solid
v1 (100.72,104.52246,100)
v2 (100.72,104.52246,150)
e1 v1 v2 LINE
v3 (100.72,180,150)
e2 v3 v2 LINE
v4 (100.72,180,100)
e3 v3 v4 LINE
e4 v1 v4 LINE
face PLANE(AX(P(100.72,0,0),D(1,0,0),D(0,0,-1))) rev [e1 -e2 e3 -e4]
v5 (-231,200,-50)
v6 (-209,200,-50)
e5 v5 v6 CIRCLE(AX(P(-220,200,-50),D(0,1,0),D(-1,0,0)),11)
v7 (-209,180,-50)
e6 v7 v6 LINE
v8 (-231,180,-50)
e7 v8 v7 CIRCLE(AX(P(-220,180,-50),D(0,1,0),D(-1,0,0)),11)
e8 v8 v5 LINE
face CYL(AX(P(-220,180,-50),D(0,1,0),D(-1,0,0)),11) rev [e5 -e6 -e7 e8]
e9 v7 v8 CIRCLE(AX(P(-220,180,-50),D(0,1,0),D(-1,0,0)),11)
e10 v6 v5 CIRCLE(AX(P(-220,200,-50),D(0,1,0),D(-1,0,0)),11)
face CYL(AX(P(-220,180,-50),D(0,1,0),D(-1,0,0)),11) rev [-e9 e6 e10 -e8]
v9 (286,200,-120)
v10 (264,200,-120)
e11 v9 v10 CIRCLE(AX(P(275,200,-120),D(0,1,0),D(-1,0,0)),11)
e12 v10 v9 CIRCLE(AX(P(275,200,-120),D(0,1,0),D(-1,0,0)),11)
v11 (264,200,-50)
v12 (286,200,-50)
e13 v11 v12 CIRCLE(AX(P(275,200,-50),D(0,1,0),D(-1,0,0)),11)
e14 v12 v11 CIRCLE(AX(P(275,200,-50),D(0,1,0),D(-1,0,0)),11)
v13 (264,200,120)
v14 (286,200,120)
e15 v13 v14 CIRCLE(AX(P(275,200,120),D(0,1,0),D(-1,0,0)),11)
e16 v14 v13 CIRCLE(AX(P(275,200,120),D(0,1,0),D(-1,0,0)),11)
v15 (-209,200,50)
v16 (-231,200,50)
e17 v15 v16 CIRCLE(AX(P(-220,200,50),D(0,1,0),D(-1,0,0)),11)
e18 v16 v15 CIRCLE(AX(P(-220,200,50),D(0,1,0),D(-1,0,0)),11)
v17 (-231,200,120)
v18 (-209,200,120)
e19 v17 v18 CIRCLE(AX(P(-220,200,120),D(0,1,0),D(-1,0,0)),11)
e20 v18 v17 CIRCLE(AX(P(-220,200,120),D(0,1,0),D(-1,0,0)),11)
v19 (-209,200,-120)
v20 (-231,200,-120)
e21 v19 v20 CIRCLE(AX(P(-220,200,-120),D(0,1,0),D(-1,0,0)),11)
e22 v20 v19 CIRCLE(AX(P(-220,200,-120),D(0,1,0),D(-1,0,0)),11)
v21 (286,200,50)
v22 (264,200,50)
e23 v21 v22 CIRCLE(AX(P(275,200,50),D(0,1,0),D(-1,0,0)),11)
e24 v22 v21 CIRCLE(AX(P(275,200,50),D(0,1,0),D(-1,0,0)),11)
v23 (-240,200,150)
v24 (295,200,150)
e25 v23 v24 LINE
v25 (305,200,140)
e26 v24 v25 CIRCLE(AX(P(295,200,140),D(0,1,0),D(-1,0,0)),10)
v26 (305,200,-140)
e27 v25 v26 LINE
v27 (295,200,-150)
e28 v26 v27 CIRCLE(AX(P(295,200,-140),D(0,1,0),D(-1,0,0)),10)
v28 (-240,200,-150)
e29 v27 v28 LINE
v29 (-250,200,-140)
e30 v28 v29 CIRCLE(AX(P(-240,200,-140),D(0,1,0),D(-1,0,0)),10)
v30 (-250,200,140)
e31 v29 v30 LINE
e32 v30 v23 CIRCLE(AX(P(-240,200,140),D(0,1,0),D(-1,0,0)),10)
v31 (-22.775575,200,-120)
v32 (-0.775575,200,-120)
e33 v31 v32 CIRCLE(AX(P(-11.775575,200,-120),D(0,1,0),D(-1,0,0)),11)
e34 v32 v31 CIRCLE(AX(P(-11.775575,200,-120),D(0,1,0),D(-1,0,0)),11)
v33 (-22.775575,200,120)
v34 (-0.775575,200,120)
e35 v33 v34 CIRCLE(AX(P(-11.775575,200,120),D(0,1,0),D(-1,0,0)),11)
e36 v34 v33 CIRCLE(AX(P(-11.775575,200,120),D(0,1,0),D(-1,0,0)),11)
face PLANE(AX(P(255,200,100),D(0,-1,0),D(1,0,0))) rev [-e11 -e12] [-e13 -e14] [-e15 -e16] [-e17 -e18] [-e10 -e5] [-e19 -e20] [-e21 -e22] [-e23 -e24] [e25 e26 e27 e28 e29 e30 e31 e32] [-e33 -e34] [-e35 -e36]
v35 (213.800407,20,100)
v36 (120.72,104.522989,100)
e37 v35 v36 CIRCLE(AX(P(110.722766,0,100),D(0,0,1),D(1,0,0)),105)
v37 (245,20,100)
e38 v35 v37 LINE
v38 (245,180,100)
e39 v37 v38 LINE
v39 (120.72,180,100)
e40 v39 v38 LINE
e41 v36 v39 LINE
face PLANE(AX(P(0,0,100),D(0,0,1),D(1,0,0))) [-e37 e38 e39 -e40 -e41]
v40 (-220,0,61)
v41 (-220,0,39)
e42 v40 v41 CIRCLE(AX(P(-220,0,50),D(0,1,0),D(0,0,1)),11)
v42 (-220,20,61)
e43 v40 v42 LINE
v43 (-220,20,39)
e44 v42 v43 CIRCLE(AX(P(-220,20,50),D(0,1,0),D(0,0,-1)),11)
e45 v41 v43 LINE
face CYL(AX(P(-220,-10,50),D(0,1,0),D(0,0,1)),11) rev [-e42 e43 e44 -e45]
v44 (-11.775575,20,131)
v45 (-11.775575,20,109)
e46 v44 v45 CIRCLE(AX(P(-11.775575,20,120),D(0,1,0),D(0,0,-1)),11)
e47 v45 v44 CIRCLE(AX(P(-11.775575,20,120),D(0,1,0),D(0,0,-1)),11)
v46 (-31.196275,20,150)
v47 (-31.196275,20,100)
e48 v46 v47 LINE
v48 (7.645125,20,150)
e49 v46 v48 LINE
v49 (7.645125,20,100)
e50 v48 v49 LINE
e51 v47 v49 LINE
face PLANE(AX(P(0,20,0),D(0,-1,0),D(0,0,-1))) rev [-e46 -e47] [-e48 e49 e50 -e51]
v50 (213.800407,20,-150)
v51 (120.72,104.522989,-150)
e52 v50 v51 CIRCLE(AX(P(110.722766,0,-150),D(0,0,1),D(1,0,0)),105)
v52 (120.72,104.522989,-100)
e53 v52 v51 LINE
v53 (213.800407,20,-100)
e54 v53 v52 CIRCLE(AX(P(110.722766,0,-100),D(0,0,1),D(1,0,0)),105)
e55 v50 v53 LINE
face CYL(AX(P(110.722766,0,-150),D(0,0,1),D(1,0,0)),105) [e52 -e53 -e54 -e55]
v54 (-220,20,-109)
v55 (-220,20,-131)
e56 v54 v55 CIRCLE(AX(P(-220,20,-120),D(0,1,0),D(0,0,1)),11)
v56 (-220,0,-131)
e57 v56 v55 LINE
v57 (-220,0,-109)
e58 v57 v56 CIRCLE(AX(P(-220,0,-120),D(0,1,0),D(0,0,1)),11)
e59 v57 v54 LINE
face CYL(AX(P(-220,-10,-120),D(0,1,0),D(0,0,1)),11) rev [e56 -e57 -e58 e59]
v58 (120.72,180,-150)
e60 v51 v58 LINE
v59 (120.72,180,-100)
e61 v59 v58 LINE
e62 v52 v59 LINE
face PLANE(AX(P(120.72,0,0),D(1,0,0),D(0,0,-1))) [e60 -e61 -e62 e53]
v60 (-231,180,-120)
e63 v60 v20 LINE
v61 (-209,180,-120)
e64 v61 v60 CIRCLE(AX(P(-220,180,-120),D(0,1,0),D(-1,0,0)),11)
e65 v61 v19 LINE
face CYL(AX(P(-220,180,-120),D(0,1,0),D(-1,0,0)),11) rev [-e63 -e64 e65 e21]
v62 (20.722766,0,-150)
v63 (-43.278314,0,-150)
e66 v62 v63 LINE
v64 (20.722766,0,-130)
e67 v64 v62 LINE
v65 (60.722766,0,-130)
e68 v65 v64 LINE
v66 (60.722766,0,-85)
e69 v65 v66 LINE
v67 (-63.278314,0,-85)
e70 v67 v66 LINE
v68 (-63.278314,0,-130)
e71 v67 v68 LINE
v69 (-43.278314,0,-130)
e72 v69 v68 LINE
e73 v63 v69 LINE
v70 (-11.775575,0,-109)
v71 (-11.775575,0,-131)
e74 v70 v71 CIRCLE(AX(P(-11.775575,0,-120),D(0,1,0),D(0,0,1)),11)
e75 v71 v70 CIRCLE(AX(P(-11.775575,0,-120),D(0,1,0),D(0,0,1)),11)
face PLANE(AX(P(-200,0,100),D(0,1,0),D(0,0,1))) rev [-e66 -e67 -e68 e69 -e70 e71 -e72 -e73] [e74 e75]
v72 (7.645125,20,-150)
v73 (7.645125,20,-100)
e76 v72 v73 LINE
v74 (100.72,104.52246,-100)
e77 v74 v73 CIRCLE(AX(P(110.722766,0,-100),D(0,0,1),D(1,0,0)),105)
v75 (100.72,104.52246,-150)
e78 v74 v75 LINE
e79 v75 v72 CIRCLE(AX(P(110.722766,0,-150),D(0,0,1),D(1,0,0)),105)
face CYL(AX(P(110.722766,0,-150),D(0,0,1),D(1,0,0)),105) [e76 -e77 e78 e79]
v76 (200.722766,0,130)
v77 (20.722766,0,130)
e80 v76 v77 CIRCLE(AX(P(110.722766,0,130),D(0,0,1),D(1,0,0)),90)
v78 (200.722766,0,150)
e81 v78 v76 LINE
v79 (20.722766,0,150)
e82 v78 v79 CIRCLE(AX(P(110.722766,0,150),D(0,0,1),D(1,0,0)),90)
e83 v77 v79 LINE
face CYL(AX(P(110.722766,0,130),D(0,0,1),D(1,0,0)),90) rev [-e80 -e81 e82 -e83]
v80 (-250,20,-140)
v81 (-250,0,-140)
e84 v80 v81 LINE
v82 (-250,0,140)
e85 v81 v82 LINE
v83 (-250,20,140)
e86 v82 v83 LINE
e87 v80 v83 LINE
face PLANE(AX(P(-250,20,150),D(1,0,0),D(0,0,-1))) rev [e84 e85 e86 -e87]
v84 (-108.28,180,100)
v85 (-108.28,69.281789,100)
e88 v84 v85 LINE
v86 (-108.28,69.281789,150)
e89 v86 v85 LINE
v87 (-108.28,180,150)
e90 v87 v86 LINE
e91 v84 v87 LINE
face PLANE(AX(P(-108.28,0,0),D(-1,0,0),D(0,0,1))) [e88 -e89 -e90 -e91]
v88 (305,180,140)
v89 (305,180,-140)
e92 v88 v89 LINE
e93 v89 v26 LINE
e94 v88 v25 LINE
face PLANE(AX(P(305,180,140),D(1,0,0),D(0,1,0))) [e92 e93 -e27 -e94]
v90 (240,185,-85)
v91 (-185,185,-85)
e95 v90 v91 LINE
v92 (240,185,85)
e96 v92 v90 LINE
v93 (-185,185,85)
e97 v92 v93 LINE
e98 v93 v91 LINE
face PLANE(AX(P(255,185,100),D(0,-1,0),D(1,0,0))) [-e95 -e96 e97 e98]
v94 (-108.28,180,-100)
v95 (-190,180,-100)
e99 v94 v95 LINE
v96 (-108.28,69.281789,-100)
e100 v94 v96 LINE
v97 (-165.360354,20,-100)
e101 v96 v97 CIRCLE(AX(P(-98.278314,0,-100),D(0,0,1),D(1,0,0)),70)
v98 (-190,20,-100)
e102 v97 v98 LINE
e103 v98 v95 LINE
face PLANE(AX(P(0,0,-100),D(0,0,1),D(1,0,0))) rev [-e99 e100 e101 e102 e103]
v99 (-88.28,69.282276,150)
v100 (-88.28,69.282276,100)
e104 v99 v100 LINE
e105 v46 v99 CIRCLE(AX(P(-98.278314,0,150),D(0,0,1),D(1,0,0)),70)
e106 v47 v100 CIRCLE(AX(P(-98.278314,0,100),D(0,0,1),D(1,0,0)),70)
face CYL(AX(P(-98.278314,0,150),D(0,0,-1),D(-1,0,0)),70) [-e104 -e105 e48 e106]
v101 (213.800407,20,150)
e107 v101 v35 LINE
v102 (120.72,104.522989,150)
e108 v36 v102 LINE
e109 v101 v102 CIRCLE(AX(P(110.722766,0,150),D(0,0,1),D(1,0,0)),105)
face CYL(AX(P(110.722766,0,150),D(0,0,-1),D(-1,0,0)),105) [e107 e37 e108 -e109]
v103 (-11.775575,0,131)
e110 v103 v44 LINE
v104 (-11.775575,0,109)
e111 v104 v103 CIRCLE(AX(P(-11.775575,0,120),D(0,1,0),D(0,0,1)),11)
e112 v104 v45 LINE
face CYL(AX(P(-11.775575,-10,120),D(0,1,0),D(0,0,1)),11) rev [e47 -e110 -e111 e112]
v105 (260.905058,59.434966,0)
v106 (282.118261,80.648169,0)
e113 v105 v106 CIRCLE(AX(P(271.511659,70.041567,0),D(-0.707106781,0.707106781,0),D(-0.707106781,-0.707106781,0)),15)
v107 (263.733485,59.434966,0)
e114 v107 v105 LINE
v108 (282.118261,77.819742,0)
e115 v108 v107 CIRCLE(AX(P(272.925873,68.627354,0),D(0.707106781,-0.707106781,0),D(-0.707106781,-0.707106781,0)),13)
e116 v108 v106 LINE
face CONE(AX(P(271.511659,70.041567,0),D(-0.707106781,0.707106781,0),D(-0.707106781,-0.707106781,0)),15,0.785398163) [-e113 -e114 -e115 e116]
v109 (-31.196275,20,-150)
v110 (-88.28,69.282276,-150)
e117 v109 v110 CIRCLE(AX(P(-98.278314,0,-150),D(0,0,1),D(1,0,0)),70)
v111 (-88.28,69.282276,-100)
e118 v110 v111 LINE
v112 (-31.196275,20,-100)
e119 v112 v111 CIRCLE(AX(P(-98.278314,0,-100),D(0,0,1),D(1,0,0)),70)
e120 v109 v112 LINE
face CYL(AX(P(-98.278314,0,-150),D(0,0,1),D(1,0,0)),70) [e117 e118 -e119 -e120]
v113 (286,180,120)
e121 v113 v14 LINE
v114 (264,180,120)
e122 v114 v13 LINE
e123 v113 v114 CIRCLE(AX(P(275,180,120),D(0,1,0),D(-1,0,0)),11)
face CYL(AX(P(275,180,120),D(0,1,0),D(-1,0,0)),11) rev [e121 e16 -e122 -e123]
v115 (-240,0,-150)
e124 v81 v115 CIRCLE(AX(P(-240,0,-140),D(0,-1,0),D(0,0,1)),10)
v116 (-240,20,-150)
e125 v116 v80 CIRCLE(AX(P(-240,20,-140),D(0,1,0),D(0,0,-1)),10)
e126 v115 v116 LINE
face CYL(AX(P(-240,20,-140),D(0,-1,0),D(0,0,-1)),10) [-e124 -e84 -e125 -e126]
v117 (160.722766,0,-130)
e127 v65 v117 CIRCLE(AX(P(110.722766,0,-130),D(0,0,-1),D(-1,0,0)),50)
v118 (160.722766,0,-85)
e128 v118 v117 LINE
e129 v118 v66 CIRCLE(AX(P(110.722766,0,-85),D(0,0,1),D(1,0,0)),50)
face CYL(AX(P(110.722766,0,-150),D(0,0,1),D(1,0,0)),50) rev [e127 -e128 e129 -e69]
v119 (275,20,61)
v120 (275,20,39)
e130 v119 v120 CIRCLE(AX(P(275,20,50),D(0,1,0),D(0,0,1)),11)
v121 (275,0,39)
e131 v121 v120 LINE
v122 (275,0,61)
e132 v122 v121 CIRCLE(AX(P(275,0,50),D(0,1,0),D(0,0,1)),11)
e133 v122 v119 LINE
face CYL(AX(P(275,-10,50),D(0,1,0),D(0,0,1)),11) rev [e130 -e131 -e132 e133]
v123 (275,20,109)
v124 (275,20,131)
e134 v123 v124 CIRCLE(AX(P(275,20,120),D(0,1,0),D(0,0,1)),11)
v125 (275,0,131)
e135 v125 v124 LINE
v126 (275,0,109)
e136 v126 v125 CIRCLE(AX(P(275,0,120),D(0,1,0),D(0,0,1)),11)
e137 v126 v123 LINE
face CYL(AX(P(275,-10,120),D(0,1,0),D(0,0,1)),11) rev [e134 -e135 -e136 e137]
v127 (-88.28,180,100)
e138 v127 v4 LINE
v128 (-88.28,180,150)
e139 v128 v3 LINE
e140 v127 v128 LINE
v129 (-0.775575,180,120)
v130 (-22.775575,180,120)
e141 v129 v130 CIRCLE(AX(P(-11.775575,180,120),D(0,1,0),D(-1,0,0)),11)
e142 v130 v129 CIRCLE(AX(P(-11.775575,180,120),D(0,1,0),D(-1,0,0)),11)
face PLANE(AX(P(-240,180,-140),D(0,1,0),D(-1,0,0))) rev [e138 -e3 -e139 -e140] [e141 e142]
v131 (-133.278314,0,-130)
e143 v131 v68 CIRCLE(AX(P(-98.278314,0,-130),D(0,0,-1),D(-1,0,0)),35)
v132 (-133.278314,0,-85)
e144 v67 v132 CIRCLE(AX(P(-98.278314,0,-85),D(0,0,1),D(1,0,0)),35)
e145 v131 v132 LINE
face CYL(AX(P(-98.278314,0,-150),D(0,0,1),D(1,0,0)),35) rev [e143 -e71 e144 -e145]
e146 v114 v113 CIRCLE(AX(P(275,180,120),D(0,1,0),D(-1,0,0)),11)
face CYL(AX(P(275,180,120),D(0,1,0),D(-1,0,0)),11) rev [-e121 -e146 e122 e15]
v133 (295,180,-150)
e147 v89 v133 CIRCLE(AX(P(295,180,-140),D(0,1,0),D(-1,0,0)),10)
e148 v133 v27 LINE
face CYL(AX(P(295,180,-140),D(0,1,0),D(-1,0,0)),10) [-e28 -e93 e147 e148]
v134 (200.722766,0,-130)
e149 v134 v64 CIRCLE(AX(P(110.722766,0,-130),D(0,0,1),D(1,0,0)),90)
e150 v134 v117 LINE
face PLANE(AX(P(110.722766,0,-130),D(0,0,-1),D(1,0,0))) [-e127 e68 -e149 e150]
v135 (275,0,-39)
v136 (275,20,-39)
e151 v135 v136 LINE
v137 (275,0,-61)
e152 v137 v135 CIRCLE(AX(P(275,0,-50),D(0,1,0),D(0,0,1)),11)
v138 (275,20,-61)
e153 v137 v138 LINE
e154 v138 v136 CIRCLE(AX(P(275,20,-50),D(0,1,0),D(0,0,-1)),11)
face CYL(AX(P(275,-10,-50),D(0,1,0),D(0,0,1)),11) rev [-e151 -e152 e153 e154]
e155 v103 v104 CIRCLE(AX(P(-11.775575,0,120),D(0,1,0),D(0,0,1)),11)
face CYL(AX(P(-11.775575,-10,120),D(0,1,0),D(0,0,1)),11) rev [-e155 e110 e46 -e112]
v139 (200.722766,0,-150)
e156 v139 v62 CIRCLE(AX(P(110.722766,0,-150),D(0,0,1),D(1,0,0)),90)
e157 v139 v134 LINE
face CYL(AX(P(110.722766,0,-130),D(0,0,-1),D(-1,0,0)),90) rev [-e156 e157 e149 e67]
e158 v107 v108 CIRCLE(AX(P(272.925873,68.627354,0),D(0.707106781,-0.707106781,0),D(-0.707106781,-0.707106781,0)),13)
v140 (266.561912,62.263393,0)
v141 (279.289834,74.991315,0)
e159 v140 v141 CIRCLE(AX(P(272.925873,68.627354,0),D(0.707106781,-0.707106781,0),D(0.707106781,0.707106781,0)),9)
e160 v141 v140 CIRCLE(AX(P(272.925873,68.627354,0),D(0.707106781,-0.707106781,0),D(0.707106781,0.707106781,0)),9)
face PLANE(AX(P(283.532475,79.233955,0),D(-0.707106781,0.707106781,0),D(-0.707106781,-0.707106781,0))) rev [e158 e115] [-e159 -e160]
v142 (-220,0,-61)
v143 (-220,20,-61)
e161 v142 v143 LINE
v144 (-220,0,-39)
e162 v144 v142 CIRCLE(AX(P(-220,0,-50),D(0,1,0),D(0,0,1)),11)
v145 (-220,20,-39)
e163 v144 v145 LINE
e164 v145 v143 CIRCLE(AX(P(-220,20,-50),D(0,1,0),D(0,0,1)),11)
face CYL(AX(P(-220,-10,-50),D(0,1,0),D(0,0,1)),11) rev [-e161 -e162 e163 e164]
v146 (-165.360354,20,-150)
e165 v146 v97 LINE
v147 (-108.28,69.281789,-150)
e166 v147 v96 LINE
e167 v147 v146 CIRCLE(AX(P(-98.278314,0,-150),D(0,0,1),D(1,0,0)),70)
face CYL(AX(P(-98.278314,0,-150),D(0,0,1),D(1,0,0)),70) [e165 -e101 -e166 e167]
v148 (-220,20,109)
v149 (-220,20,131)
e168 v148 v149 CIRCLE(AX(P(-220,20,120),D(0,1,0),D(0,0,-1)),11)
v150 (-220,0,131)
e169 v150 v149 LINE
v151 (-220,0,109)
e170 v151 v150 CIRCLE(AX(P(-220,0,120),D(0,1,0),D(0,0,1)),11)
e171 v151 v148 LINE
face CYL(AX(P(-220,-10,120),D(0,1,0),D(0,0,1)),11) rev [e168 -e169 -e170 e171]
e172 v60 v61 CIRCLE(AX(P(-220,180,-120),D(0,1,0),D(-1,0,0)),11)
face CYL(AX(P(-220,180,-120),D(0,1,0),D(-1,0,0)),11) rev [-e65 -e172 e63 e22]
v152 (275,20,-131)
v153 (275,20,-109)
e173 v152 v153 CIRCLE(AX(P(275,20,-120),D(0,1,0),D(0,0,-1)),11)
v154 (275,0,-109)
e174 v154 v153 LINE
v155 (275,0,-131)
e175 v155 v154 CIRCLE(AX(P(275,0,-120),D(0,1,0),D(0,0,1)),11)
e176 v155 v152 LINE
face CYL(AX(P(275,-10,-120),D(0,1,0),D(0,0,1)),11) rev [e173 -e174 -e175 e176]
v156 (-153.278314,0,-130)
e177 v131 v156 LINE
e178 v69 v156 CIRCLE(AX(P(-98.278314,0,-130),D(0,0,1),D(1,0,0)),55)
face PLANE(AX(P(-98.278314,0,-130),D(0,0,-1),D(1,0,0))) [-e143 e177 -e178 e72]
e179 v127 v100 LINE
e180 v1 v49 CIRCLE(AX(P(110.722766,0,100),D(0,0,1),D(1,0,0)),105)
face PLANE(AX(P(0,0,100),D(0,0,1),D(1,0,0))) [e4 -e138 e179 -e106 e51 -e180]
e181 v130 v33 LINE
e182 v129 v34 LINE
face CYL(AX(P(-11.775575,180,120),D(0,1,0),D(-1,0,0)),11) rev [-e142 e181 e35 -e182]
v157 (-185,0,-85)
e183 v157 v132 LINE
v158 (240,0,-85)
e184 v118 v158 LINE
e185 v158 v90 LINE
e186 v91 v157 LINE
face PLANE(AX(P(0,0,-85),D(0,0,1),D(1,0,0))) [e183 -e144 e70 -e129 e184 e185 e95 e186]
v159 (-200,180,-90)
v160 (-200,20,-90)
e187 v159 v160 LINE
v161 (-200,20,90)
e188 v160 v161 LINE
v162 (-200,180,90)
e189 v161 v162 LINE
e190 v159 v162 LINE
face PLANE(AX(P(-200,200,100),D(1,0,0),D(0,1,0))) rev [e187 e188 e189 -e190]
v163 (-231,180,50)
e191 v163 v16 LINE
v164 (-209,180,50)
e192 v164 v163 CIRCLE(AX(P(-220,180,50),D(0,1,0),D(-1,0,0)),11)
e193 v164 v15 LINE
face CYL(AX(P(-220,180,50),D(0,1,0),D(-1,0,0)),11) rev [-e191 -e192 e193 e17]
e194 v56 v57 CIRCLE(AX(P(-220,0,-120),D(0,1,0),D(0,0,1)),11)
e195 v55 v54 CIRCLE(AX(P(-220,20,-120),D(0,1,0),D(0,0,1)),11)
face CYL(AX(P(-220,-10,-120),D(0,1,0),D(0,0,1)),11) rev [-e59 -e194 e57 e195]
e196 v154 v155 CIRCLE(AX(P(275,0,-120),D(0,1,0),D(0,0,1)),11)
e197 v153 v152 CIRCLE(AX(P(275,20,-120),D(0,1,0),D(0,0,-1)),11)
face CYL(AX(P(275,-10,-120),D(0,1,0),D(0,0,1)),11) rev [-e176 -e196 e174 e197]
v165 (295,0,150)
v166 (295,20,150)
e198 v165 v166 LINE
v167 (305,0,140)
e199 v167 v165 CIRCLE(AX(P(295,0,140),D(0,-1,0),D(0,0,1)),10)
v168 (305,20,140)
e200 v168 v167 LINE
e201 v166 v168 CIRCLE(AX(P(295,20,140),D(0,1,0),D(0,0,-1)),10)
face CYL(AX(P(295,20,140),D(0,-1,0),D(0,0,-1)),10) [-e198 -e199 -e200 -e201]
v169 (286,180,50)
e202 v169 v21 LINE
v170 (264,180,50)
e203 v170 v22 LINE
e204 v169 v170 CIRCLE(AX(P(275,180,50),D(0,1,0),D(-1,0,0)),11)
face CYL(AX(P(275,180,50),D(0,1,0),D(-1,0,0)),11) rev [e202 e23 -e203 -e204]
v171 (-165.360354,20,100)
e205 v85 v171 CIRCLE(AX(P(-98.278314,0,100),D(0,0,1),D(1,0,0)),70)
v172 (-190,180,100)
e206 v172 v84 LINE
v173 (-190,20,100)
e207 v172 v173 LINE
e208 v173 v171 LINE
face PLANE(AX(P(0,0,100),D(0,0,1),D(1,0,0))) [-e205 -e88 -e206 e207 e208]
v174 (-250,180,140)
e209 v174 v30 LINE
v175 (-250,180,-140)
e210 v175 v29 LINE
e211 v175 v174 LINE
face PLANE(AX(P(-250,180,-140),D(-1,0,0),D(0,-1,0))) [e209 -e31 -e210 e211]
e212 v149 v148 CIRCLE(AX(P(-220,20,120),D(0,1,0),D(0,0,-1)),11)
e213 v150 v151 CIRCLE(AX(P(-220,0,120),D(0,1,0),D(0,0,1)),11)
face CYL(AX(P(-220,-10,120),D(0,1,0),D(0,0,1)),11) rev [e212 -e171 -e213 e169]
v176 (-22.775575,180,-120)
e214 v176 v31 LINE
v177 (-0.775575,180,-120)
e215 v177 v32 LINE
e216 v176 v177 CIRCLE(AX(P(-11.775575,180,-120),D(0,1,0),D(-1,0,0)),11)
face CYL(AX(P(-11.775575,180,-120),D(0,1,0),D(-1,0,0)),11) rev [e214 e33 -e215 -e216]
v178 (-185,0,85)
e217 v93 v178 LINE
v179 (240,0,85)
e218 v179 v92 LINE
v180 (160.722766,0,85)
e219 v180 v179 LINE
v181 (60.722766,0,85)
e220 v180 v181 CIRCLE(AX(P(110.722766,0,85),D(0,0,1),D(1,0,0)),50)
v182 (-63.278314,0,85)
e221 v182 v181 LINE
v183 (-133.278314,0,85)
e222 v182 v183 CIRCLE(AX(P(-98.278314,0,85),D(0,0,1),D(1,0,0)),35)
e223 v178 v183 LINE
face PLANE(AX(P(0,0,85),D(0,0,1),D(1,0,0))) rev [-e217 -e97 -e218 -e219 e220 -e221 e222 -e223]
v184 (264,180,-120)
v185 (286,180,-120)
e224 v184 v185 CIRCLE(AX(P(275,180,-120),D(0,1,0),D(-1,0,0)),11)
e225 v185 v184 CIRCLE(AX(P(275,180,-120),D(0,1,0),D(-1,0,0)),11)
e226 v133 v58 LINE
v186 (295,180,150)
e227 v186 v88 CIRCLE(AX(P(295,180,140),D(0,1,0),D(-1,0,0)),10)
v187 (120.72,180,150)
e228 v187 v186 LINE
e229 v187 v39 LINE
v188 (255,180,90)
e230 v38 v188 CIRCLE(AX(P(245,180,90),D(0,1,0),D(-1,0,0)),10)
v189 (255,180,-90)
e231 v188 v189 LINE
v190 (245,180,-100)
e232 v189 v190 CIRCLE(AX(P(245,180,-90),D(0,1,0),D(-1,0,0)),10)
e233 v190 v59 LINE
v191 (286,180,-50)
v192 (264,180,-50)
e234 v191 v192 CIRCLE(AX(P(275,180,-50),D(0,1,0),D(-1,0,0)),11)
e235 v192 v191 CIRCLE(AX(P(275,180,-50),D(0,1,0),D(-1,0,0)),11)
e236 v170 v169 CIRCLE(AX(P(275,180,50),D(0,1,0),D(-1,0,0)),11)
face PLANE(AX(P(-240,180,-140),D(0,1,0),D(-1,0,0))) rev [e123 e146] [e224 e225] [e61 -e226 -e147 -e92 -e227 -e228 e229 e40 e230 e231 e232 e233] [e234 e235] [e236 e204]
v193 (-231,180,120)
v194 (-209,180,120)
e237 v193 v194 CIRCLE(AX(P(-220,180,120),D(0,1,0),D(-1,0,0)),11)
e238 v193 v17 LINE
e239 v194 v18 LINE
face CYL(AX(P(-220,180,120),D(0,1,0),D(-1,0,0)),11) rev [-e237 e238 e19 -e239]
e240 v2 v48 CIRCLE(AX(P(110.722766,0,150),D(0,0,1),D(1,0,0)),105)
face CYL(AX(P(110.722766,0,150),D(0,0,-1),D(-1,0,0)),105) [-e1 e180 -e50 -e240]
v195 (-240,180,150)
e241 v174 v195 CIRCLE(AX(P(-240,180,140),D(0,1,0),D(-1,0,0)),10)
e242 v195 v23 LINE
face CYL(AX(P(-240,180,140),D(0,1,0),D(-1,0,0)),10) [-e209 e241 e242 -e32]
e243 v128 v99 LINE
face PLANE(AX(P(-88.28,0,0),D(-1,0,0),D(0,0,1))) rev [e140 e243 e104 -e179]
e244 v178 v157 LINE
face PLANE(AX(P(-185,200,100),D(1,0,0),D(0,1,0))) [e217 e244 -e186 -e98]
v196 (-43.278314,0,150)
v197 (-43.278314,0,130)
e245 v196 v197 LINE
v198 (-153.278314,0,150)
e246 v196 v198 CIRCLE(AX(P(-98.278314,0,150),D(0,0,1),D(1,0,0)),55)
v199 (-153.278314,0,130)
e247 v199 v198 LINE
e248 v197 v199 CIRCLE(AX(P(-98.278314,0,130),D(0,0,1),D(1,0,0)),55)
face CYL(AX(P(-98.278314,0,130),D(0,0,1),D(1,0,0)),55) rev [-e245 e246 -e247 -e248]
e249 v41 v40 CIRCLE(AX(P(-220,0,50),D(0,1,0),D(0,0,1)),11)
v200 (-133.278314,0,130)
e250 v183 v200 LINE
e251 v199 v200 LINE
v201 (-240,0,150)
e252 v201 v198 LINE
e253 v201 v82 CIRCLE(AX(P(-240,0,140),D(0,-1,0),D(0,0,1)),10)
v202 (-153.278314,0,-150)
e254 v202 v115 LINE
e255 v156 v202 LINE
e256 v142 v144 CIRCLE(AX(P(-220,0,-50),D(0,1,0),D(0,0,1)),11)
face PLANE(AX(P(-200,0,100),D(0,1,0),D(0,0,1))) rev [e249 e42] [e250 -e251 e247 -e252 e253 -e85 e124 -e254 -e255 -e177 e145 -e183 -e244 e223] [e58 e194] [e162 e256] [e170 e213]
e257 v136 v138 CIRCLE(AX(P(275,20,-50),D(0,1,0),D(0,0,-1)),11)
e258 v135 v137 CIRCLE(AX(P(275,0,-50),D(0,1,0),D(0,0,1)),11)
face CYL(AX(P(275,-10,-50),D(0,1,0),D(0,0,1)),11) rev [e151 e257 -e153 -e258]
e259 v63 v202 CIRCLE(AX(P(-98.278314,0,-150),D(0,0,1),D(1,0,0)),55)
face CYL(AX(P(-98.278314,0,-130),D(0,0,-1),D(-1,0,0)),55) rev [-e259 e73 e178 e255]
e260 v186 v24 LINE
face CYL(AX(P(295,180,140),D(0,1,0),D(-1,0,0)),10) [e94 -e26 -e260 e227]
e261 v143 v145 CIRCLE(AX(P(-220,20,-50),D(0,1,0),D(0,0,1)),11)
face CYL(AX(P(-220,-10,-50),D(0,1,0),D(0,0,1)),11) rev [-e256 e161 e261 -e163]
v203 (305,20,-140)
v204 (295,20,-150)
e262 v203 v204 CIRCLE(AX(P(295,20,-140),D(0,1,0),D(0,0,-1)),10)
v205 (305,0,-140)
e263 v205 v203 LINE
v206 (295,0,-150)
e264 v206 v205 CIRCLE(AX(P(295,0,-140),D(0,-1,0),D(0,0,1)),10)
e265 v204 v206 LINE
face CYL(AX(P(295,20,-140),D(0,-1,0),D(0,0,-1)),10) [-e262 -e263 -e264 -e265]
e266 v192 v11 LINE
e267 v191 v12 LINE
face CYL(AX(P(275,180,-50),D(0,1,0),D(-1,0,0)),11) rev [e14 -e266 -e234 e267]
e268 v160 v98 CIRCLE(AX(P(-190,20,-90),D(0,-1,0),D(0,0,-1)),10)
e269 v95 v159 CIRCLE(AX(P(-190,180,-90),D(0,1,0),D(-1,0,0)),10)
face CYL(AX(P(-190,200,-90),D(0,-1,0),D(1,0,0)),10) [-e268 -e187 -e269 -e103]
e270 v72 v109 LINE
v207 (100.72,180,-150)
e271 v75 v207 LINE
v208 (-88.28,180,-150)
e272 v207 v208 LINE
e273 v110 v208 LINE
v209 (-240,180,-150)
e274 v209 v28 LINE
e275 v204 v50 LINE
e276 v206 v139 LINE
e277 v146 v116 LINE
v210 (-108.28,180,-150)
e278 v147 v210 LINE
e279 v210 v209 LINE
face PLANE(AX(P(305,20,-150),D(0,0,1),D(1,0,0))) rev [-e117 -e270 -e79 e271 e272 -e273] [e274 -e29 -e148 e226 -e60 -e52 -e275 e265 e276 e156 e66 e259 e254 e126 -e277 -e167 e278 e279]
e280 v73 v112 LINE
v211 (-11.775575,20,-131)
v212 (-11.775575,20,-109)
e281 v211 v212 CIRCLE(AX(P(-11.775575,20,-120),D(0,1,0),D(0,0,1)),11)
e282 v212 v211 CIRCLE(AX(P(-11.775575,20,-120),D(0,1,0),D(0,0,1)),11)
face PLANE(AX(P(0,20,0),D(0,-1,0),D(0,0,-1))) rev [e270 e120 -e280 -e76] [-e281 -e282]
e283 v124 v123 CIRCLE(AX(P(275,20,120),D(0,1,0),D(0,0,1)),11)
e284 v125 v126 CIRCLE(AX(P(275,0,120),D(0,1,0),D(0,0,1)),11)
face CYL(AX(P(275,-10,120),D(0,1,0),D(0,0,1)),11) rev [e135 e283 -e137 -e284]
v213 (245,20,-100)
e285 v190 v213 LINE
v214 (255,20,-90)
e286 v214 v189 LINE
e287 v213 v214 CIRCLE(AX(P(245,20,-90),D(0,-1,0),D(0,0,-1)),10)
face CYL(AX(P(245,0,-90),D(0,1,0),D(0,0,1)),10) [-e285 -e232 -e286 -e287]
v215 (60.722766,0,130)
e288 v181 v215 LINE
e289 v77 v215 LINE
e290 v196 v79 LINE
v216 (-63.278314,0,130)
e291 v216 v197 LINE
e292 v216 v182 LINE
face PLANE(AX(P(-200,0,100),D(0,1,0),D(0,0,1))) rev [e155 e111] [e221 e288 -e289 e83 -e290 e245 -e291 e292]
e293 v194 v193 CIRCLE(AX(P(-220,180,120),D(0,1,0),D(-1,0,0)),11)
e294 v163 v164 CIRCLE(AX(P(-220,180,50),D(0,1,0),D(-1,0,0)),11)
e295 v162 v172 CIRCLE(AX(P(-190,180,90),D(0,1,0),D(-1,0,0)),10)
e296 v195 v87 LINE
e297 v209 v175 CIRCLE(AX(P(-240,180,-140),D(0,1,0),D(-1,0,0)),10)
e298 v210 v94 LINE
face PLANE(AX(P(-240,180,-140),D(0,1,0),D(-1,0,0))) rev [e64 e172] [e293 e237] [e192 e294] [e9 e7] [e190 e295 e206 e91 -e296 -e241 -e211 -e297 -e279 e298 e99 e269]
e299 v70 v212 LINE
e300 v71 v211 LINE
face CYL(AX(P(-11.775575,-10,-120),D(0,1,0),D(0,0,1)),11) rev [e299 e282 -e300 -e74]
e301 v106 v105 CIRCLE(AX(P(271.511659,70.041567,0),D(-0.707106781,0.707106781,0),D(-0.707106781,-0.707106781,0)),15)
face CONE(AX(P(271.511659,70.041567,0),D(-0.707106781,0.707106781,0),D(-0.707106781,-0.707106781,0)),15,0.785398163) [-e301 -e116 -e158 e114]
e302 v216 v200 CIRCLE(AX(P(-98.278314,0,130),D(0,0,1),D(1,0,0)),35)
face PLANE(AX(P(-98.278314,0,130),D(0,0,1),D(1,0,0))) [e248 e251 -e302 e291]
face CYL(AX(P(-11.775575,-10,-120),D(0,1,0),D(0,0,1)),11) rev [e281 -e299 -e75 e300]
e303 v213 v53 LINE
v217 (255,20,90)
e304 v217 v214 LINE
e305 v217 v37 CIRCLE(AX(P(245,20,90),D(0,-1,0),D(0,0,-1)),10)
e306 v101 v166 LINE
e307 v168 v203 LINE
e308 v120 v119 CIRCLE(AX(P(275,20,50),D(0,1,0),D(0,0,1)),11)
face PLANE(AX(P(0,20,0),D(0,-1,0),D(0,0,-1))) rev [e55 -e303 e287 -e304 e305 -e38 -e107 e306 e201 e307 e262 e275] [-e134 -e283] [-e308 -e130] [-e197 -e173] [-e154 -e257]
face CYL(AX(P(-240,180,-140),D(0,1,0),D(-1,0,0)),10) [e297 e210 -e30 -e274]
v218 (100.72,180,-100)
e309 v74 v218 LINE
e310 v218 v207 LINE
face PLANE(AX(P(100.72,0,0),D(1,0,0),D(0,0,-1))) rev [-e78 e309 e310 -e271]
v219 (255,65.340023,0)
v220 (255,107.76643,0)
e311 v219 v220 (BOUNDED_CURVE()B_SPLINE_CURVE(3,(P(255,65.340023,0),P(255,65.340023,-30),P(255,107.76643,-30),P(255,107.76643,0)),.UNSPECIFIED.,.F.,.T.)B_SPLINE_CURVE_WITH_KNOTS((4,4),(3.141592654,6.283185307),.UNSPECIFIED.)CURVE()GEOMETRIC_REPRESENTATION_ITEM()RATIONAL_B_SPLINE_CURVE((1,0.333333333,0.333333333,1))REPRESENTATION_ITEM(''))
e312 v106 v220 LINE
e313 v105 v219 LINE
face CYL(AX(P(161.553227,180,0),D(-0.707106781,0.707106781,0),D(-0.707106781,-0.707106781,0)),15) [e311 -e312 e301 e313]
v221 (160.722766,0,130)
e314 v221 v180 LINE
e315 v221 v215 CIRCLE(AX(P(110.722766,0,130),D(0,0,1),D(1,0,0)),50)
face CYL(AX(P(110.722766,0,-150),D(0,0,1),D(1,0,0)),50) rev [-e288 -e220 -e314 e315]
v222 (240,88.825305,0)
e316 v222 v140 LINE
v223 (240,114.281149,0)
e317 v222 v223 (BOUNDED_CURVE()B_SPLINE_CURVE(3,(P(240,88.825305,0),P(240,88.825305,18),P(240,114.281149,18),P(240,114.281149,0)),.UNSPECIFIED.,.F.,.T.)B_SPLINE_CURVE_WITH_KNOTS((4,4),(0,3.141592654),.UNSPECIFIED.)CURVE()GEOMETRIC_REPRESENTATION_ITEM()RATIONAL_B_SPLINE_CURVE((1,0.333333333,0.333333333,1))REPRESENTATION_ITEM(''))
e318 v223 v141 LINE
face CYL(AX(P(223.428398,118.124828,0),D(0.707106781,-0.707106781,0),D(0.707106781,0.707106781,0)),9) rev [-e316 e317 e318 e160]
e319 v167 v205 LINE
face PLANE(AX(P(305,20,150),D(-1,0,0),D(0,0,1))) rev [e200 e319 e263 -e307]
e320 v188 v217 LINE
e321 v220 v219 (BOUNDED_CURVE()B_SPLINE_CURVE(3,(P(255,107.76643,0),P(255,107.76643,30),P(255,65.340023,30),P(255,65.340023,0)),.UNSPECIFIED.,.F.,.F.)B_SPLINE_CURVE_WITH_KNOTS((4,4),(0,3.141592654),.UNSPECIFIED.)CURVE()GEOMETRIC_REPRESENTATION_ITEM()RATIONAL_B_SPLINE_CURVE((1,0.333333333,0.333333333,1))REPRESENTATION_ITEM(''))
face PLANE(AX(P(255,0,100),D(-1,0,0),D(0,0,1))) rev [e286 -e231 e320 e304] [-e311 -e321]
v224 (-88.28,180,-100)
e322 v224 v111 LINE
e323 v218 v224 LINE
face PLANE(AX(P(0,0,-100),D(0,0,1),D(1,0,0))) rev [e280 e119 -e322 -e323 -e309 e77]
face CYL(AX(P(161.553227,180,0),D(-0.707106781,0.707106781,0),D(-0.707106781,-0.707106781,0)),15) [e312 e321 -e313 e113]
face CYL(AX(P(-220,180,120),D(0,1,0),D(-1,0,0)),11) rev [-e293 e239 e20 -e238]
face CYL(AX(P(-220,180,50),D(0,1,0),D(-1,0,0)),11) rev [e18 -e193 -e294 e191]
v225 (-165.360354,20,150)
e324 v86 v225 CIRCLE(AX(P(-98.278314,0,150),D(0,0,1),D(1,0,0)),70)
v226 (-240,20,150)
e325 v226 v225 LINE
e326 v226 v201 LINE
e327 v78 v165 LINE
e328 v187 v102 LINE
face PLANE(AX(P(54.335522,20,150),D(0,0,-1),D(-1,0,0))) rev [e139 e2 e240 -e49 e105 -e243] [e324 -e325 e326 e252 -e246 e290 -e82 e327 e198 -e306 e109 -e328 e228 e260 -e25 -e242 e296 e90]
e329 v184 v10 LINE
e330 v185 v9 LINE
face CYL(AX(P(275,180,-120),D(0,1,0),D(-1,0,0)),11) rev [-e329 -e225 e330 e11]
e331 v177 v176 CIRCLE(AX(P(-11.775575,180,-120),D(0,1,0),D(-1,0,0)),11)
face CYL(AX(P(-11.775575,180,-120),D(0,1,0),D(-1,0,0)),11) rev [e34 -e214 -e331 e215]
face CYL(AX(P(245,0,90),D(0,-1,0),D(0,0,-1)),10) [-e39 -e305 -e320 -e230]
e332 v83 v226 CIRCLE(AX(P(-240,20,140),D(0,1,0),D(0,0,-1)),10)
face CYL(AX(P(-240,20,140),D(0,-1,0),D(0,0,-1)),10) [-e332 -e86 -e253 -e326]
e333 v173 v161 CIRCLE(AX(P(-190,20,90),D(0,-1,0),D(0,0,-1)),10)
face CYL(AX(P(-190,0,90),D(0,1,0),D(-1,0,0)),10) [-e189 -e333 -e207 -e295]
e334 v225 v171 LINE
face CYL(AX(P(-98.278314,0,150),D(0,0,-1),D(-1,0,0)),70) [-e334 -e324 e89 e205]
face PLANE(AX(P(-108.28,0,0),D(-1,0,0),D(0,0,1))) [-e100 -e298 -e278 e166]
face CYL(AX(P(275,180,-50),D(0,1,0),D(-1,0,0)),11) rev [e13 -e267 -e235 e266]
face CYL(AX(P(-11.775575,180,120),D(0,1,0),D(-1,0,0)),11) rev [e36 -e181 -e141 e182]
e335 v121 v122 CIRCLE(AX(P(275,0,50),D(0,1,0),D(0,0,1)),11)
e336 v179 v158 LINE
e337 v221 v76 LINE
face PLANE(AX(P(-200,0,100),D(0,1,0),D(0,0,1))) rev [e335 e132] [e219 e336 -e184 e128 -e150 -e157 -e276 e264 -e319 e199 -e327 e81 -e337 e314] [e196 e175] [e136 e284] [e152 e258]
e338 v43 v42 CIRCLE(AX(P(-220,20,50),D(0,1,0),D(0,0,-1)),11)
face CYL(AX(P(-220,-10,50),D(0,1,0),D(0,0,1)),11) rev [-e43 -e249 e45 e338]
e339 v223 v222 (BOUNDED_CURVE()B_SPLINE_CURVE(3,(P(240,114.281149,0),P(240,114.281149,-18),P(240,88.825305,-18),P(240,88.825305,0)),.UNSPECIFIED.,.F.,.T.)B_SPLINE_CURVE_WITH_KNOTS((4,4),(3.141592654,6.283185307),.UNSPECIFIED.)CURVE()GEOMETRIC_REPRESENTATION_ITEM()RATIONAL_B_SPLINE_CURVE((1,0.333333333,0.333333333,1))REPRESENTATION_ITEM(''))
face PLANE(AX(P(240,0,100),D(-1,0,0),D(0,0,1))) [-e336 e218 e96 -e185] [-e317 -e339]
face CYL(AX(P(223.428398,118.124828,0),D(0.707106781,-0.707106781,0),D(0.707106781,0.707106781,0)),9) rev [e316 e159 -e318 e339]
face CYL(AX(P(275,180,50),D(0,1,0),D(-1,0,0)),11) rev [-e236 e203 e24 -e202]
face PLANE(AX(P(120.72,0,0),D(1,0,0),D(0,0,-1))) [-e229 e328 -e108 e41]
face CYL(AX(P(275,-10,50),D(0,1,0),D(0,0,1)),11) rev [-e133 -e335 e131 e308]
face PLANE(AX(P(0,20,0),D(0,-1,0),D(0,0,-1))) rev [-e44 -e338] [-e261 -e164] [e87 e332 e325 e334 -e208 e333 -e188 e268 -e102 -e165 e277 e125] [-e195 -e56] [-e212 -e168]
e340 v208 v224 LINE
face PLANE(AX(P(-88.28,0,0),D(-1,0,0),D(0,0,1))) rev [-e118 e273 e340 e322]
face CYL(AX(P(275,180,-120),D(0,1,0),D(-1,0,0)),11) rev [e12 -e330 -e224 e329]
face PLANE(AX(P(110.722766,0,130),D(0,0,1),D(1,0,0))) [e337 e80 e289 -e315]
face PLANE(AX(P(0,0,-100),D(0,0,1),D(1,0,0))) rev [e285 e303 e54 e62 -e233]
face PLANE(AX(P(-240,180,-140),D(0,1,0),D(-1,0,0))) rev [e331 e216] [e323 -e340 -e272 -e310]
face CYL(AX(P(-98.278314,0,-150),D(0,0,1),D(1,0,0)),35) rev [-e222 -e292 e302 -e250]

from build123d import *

# Parameters (mm, degrees)
SKETCH1_W           = 455
SKETCH1_H           = 200
BOSS_EXTRUDE1_DEPTH = 100
SHELL1_T            = -15
BOSS_EXTRUDE2_DEPTH = 20
BOSS_EXTRUDE3_DEPTH = 50
SKETCH4_R           = 90
SKETCH4_R_2         = 55
CUT_EXTRUDE1_DEPTH  = 20
SKETCH5_R           = 35
SKETCH5_R_2         = 50
CUT_EXTRUDE3_DEPTH  = 460.809743263
FILLET1_R           = 10
SKETCH6_R           = 11
CUT_EXTRUDE4_DEPTH  = 30
SKETCH7_R           = 11
BOSS_EXTRUDE4_DEPTH = 20
BOSS_EXTRUDE5_DEPTH = 10
SKETCH9_W           = 55.431100879
SKETCH9_H           = 127.178864335
BOSS_EXTRUDE6_DEPTH = 10
SKETCH11_R          = 9
CUT_EXTRUDE5_DEPTH  = 70
SKETCH12_W          = 79.277233939
SKETCH12_H          = 170
CUT_EXTRUDE6_DEPTH  = 130
CHAMFER1_SIZE       = 2


with BuildPart() as part:
    # Sketch1 → Boss-Extrude1 (new, symmetric)
    with BuildSketch(Plane.XY):
        with Locations((27.5, 100)):
            Rectangle(SKETCH1_W, SKETCH1_H)
    extrude(amount=BOSS_EXTRUDE1_DEPTH, both=True)

    # Shell1
    shell1_openings = [part.faces().sort_by_distance(p)[0] for p in [
        (27.5, 0, 0),
    ]]
    offset(amount=SHELL1_T, openings=shell1_openings, kind=Kind.INTERSECTION)

    # Sketch2 → Boss-Extrude2 (add)
    with BuildSketch(Plane(origin=(0, 0, 0), x_dir=(1, 0, 0), z_dir=(0, 1, 0))):
        Polygon((-114.985807422, 150), (-250, 150), (-250, -150), (-114.985807422, -150), (54.335521535, -150), (305, -150), (305, 150), (54.335521535, 150), align=None)
        Polygon((-114.985807422, 100), (-200, 100), (-200, -100), (-114.985807422, -100), (54.335521535, -100), (255, -100), (255, 100), (54.335521535, 100), align=None, mode=Mode.SUBTRACT)
    extrude(amount=BOSS_EXTRUDE2_DEPTH)

    # Sketch3 → Boss-Extrude3 (add)
    with BuildSketch(Plane.XY.offset(100)):
        with BuildLine():
            ThreePointArc((213.800406701, 20), (110.722766061, 105), (7.645125421, 20))
            Line((7.645125421, 20), (213.800406701, 20))
        make_face()
        with BuildLine():
            ThreePointArc((-31.196275144, 20), (-98.278314469, 70), (-165.360353794, 20))
            Line((-165.360353794, 20), (-31.196275144, 20))
        make_face()
    boss_extrude3 = extrude(amount=BOSS_EXTRUDE3_DEPTH)

    # Sketch4 → Cut-Extrude1 (cut)
    with BuildSketch(Plane.XY.offset(150)):
        with Locations((110.722766061, 0)):
            Circle(SKETCH4_R)
        with Locations((-98.278314469, 0)):
            Circle(SKETCH4_R_2)
    cut_extrude1 = extrude(amount=-CUT_EXTRUDE1_DEPTH, mode=Mode.SUBTRACT)

    # Mirror1: Boss-Extrude3, Cut-Extrude1 across plane
    add(boss_extrude3.mirror(Plane.XY))
    add(cut_extrude1.mirror(Plane.XY), mode=Mode.SUBTRACT)

    # Sketch5 → Cut-Extrude3 (cut, through all)
    with BuildSketch(Plane.XY.offset(130)):
        with Locations((-98.278314469, 0)):
            Circle(SKETCH5_R)
        with Locations((110.722766061, 0)):
            Circle(SKETCH5_R_2)
    extrude(amount=-CUT_EXTRUDE3_DEPTH, mode=Mode.SUBTRACT)

    # Fillet1
    fillet1_edges = [part.edges().sort_by_distance(p)[0] for p in [
        (-200, 110, 100),
        (255, 110, -100),
        (255, 110, 100),
        (-250, 10, -150),
        (-250, 10, 150),
        (305, 10, 150),
        (305, 10, -150),
        (-200, 110, -100),
    ]]
    fillet(fillet1_edges, radius=FILLET1_R)

    # Sketch6 → Cut-Extrude4 (cut)
    with BuildSketch(Plane(origin=(0, 20, 0), x_dir=(1, 0, 0), z_dir=(0, 1, 0))):
        with Locations(Location((-220, 120, 0), (0, 0, 270))):
            Circle(SKETCH6_R)
        with Locations(Location((-220, 50, 0), (0, 0, 270))):
            Circle(SKETCH6_R)
        with Locations(Location((-220, -50, 0), (0, 0, 270))):
            Circle(SKETCH6_R)
        with Locations(Location((-220, -120, 0), (0, 0, 270))):
            Circle(SKETCH6_R)
        with Locations(Location((275, -120, 0), (0, 0, 270))):
            Circle(SKETCH6_R)
        with Locations(Location((275, -50, 0), (0, 0, 270))):
            Circle(SKETCH6_R)
        with Locations(Location((275, 50, 0), (0, 0, 270))):
            Circle(SKETCH6_R)
        with Locations(Location((275, 120, 0), (0, 0, 270))):
            Circle(SKETCH6_R)
        with Locations(Location((-11.775574862, 120, 0), (0, 0, 270))):
            Circle(SKETCH6_R)
        with Locations(Location((-11.775574862, -120, 0), (0, 0, 270))):
            Circle(SKETCH6_R)
    extrude(amount=-CUT_EXTRUDE4_DEPTH, mode=Mode.SUBTRACT)

    # Sketch7 → Boss-Extrude4 (add)
    with BuildSketch(Plane(origin=(0, 200, 0), x_dir=(1, 0, 0), z_dir=(0, 1, 0))):
        with BuildLine():
            Line((-165.360353794, 150), (-240, 150))
            ThreePointArc((-240, 150), (-247.071067812, 147.071067812), (-250, 140))
            Line((-250, 140), (-250, -140))
            ThreePointArc((-250, -140), (-247.071067812, -147.071067812), (-240, -150))
            Line((-240, -150), (-165.360353794, -150))
            Line((-165.360353794, -150), (-31.196275144, -150))
            Line((-31.196275144, -150), (7.645125421, -150))
            Line((7.645125421, -150), (213.800406701, -150))
            Line((213.800406701, -150), (295, -150))
            ThreePointArc((295, -150), (302.071067812, -147.071067812), (305, -140))
            Line((305, -140), (305, 140))
            ThreePointArc((305, 140), (302.071067812, 147.071067812), (295, 150))
            Line((295, 150), (213.800406701, 150))
            Line((213.800406701, 150), (7.645125421, 150))
            Line((7.645125421, 150), (-31.196275144, 150))
            Line((-31.196275144, 150), (-165.360353794, 150))
        make_face()
        with Locations(Location((-220, 120, 0), (0, 0, 270))):
            Circle(SKETCH7_R, mode=Mode.SUBTRACT)
        with Locations(Location((-220, 50, 0), (0, 0, 270))):
            Circle(SKETCH7_R, mode=Mode.SUBTRACT)
        with Locations(Location((-220, -50, 0), (0, 0, 270))):
            Circle(SKETCH7_R, mode=Mode.SUBTRACT)
        with Locations(Location((-220, -120, 0), (0, 0, 270))):
            Circle(SKETCH7_R, mode=Mode.SUBTRACT)
        with Locations(Location((-11.775574862, -120, 0), (0, 0, 270))):
            Circle(SKETCH7_R, mode=Mode.SUBTRACT)
        with Locations(Location((-11.775574862, 120, 0), (0, 0, 270))):
            Circle(SKETCH7_R, mode=Mode.SUBTRACT)
        with Locations(Location((275, 120, 0), (0, 0, 270))):
            Circle(SKETCH7_R, mode=Mode.SUBTRACT)
        with Locations(Location((275, 50, 0), (0, 0, 270))):
            Circle(SKETCH7_R, mode=Mode.SUBTRACT)
        with Locations(Location((275, -50, 0), (0, 0, 270))):
            Circle(SKETCH7_R, mode=Mode.SUBTRACT)
        with Locations(Location((275, -120, 0), (0, 0, 270))):
            Circle(SKETCH7_R, mode=Mode.SUBTRACT)
        with BuildLine():
            Line((245, 100), (-190, 100))
            ThreePointArc((-190, 100), (-197.071067812, 97.071067812), (-200, 90))
            Line((-200, 90), (-200, -90))
            ThreePointArc((-200, -90), (-197.071067812, -97.071067812), (-190, -100))
            Line((-190, -100), (245, -100))
            ThreePointArc((245, -100), (252.071067812, -97.071067812), (255, -90))
            Line((255, -90), (255, 90))
            ThreePointArc((255, 90), (252.071067812, 97.071067812), (245, 100))
        make_face(mode=Mode.SUBTRACT)
    extrude(amount=-BOSS_EXTRUDE4_DEPTH)

    # Sketch8 → Boss-Extrude5 (add, symmetric)
    with BuildSketch(Plane(origin=(110.72, 0, 0), x_dir=(0, 0, -1), z_dir=(1, 0, 0))):
        Polygon((100, 100), (150, 100), (150, 184.754608039), (95.891627804, 184.754608039), align=None)
        Polygon((-95.891627804, 184.754608039), (-100, 100), (-150, 100), (-150, 184.754608039), align=None)
    extrude(amount=BOSS_EXTRUDE5_DEPTH, both=True)

    # Sketch9 → Boss-Extrude6 (add, symmetric)
    with BuildSketch(Plane(origin=(-98.28, 0, 0), x_dir=(0, 0, -1), z_dir=(1, 0, 0))):
        with Locations((122.284449561, 122.079617257)):
            Rectangle(SKETCH9_W, SKETCH9_H)
        with Locations((-122.284449561, 122.079617257)):
            Rectangle(SKETCH9_W, SKETCH9_H)
    extrude(amount=BOSS_EXTRUDE6_DEPTH, both=True)

    # Sketch10 → Revolve1 (revolve)
    with BuildSketch(Plane.XY):
        Polygon((243.881987677, 118.884442333), (283.532474552, 79.233955458), (272.925872834, 68.62735374), (233.155728657, 108.397497917), align=None)
    revolve(axis=Axis((161.553226574, 180, 0), (0.7071067811865464, -0.7071067811865488, 0)))

    # Sketch11 → Cut-Extrude5 (cut)
    with BuildSketch(Plane(origin=(102.149259547, -102.149259547, 0), x_dir=(0, 0, -1), z_dir=(0.7071067811865465, -0.7071067811865487, 0))):
        with Locations(Location((0, 241.514602646, 0), (0, 0, 90))):
            Circle(SKETCH11_R)
    extrude(amount=-CUT_EXTRUDE5_DEPTH, mode=Mode.SUBTRACT)

    # Sketch12 → Cut-Extrude6 (cut)
    with BuildSketch(Plane.XZ):
        with Locations((200.361383031, 0)):
            Rectangle(SKETCH12_W, SKETCH12_H)
    extrude(amount=-CUT_EXTRUDE6_DEPTH, mode=Mode.SUBTRACT)

    # Chamfer1
    chamfer1_edges = [part.edges().sort_by_distance(p)[0] for p in [
        (262.319271116, 58.020752022, 0),
    ]]
    chamfer(chamfer1_edges, length=CHAMFER1_SIZE)


solid = part.part
